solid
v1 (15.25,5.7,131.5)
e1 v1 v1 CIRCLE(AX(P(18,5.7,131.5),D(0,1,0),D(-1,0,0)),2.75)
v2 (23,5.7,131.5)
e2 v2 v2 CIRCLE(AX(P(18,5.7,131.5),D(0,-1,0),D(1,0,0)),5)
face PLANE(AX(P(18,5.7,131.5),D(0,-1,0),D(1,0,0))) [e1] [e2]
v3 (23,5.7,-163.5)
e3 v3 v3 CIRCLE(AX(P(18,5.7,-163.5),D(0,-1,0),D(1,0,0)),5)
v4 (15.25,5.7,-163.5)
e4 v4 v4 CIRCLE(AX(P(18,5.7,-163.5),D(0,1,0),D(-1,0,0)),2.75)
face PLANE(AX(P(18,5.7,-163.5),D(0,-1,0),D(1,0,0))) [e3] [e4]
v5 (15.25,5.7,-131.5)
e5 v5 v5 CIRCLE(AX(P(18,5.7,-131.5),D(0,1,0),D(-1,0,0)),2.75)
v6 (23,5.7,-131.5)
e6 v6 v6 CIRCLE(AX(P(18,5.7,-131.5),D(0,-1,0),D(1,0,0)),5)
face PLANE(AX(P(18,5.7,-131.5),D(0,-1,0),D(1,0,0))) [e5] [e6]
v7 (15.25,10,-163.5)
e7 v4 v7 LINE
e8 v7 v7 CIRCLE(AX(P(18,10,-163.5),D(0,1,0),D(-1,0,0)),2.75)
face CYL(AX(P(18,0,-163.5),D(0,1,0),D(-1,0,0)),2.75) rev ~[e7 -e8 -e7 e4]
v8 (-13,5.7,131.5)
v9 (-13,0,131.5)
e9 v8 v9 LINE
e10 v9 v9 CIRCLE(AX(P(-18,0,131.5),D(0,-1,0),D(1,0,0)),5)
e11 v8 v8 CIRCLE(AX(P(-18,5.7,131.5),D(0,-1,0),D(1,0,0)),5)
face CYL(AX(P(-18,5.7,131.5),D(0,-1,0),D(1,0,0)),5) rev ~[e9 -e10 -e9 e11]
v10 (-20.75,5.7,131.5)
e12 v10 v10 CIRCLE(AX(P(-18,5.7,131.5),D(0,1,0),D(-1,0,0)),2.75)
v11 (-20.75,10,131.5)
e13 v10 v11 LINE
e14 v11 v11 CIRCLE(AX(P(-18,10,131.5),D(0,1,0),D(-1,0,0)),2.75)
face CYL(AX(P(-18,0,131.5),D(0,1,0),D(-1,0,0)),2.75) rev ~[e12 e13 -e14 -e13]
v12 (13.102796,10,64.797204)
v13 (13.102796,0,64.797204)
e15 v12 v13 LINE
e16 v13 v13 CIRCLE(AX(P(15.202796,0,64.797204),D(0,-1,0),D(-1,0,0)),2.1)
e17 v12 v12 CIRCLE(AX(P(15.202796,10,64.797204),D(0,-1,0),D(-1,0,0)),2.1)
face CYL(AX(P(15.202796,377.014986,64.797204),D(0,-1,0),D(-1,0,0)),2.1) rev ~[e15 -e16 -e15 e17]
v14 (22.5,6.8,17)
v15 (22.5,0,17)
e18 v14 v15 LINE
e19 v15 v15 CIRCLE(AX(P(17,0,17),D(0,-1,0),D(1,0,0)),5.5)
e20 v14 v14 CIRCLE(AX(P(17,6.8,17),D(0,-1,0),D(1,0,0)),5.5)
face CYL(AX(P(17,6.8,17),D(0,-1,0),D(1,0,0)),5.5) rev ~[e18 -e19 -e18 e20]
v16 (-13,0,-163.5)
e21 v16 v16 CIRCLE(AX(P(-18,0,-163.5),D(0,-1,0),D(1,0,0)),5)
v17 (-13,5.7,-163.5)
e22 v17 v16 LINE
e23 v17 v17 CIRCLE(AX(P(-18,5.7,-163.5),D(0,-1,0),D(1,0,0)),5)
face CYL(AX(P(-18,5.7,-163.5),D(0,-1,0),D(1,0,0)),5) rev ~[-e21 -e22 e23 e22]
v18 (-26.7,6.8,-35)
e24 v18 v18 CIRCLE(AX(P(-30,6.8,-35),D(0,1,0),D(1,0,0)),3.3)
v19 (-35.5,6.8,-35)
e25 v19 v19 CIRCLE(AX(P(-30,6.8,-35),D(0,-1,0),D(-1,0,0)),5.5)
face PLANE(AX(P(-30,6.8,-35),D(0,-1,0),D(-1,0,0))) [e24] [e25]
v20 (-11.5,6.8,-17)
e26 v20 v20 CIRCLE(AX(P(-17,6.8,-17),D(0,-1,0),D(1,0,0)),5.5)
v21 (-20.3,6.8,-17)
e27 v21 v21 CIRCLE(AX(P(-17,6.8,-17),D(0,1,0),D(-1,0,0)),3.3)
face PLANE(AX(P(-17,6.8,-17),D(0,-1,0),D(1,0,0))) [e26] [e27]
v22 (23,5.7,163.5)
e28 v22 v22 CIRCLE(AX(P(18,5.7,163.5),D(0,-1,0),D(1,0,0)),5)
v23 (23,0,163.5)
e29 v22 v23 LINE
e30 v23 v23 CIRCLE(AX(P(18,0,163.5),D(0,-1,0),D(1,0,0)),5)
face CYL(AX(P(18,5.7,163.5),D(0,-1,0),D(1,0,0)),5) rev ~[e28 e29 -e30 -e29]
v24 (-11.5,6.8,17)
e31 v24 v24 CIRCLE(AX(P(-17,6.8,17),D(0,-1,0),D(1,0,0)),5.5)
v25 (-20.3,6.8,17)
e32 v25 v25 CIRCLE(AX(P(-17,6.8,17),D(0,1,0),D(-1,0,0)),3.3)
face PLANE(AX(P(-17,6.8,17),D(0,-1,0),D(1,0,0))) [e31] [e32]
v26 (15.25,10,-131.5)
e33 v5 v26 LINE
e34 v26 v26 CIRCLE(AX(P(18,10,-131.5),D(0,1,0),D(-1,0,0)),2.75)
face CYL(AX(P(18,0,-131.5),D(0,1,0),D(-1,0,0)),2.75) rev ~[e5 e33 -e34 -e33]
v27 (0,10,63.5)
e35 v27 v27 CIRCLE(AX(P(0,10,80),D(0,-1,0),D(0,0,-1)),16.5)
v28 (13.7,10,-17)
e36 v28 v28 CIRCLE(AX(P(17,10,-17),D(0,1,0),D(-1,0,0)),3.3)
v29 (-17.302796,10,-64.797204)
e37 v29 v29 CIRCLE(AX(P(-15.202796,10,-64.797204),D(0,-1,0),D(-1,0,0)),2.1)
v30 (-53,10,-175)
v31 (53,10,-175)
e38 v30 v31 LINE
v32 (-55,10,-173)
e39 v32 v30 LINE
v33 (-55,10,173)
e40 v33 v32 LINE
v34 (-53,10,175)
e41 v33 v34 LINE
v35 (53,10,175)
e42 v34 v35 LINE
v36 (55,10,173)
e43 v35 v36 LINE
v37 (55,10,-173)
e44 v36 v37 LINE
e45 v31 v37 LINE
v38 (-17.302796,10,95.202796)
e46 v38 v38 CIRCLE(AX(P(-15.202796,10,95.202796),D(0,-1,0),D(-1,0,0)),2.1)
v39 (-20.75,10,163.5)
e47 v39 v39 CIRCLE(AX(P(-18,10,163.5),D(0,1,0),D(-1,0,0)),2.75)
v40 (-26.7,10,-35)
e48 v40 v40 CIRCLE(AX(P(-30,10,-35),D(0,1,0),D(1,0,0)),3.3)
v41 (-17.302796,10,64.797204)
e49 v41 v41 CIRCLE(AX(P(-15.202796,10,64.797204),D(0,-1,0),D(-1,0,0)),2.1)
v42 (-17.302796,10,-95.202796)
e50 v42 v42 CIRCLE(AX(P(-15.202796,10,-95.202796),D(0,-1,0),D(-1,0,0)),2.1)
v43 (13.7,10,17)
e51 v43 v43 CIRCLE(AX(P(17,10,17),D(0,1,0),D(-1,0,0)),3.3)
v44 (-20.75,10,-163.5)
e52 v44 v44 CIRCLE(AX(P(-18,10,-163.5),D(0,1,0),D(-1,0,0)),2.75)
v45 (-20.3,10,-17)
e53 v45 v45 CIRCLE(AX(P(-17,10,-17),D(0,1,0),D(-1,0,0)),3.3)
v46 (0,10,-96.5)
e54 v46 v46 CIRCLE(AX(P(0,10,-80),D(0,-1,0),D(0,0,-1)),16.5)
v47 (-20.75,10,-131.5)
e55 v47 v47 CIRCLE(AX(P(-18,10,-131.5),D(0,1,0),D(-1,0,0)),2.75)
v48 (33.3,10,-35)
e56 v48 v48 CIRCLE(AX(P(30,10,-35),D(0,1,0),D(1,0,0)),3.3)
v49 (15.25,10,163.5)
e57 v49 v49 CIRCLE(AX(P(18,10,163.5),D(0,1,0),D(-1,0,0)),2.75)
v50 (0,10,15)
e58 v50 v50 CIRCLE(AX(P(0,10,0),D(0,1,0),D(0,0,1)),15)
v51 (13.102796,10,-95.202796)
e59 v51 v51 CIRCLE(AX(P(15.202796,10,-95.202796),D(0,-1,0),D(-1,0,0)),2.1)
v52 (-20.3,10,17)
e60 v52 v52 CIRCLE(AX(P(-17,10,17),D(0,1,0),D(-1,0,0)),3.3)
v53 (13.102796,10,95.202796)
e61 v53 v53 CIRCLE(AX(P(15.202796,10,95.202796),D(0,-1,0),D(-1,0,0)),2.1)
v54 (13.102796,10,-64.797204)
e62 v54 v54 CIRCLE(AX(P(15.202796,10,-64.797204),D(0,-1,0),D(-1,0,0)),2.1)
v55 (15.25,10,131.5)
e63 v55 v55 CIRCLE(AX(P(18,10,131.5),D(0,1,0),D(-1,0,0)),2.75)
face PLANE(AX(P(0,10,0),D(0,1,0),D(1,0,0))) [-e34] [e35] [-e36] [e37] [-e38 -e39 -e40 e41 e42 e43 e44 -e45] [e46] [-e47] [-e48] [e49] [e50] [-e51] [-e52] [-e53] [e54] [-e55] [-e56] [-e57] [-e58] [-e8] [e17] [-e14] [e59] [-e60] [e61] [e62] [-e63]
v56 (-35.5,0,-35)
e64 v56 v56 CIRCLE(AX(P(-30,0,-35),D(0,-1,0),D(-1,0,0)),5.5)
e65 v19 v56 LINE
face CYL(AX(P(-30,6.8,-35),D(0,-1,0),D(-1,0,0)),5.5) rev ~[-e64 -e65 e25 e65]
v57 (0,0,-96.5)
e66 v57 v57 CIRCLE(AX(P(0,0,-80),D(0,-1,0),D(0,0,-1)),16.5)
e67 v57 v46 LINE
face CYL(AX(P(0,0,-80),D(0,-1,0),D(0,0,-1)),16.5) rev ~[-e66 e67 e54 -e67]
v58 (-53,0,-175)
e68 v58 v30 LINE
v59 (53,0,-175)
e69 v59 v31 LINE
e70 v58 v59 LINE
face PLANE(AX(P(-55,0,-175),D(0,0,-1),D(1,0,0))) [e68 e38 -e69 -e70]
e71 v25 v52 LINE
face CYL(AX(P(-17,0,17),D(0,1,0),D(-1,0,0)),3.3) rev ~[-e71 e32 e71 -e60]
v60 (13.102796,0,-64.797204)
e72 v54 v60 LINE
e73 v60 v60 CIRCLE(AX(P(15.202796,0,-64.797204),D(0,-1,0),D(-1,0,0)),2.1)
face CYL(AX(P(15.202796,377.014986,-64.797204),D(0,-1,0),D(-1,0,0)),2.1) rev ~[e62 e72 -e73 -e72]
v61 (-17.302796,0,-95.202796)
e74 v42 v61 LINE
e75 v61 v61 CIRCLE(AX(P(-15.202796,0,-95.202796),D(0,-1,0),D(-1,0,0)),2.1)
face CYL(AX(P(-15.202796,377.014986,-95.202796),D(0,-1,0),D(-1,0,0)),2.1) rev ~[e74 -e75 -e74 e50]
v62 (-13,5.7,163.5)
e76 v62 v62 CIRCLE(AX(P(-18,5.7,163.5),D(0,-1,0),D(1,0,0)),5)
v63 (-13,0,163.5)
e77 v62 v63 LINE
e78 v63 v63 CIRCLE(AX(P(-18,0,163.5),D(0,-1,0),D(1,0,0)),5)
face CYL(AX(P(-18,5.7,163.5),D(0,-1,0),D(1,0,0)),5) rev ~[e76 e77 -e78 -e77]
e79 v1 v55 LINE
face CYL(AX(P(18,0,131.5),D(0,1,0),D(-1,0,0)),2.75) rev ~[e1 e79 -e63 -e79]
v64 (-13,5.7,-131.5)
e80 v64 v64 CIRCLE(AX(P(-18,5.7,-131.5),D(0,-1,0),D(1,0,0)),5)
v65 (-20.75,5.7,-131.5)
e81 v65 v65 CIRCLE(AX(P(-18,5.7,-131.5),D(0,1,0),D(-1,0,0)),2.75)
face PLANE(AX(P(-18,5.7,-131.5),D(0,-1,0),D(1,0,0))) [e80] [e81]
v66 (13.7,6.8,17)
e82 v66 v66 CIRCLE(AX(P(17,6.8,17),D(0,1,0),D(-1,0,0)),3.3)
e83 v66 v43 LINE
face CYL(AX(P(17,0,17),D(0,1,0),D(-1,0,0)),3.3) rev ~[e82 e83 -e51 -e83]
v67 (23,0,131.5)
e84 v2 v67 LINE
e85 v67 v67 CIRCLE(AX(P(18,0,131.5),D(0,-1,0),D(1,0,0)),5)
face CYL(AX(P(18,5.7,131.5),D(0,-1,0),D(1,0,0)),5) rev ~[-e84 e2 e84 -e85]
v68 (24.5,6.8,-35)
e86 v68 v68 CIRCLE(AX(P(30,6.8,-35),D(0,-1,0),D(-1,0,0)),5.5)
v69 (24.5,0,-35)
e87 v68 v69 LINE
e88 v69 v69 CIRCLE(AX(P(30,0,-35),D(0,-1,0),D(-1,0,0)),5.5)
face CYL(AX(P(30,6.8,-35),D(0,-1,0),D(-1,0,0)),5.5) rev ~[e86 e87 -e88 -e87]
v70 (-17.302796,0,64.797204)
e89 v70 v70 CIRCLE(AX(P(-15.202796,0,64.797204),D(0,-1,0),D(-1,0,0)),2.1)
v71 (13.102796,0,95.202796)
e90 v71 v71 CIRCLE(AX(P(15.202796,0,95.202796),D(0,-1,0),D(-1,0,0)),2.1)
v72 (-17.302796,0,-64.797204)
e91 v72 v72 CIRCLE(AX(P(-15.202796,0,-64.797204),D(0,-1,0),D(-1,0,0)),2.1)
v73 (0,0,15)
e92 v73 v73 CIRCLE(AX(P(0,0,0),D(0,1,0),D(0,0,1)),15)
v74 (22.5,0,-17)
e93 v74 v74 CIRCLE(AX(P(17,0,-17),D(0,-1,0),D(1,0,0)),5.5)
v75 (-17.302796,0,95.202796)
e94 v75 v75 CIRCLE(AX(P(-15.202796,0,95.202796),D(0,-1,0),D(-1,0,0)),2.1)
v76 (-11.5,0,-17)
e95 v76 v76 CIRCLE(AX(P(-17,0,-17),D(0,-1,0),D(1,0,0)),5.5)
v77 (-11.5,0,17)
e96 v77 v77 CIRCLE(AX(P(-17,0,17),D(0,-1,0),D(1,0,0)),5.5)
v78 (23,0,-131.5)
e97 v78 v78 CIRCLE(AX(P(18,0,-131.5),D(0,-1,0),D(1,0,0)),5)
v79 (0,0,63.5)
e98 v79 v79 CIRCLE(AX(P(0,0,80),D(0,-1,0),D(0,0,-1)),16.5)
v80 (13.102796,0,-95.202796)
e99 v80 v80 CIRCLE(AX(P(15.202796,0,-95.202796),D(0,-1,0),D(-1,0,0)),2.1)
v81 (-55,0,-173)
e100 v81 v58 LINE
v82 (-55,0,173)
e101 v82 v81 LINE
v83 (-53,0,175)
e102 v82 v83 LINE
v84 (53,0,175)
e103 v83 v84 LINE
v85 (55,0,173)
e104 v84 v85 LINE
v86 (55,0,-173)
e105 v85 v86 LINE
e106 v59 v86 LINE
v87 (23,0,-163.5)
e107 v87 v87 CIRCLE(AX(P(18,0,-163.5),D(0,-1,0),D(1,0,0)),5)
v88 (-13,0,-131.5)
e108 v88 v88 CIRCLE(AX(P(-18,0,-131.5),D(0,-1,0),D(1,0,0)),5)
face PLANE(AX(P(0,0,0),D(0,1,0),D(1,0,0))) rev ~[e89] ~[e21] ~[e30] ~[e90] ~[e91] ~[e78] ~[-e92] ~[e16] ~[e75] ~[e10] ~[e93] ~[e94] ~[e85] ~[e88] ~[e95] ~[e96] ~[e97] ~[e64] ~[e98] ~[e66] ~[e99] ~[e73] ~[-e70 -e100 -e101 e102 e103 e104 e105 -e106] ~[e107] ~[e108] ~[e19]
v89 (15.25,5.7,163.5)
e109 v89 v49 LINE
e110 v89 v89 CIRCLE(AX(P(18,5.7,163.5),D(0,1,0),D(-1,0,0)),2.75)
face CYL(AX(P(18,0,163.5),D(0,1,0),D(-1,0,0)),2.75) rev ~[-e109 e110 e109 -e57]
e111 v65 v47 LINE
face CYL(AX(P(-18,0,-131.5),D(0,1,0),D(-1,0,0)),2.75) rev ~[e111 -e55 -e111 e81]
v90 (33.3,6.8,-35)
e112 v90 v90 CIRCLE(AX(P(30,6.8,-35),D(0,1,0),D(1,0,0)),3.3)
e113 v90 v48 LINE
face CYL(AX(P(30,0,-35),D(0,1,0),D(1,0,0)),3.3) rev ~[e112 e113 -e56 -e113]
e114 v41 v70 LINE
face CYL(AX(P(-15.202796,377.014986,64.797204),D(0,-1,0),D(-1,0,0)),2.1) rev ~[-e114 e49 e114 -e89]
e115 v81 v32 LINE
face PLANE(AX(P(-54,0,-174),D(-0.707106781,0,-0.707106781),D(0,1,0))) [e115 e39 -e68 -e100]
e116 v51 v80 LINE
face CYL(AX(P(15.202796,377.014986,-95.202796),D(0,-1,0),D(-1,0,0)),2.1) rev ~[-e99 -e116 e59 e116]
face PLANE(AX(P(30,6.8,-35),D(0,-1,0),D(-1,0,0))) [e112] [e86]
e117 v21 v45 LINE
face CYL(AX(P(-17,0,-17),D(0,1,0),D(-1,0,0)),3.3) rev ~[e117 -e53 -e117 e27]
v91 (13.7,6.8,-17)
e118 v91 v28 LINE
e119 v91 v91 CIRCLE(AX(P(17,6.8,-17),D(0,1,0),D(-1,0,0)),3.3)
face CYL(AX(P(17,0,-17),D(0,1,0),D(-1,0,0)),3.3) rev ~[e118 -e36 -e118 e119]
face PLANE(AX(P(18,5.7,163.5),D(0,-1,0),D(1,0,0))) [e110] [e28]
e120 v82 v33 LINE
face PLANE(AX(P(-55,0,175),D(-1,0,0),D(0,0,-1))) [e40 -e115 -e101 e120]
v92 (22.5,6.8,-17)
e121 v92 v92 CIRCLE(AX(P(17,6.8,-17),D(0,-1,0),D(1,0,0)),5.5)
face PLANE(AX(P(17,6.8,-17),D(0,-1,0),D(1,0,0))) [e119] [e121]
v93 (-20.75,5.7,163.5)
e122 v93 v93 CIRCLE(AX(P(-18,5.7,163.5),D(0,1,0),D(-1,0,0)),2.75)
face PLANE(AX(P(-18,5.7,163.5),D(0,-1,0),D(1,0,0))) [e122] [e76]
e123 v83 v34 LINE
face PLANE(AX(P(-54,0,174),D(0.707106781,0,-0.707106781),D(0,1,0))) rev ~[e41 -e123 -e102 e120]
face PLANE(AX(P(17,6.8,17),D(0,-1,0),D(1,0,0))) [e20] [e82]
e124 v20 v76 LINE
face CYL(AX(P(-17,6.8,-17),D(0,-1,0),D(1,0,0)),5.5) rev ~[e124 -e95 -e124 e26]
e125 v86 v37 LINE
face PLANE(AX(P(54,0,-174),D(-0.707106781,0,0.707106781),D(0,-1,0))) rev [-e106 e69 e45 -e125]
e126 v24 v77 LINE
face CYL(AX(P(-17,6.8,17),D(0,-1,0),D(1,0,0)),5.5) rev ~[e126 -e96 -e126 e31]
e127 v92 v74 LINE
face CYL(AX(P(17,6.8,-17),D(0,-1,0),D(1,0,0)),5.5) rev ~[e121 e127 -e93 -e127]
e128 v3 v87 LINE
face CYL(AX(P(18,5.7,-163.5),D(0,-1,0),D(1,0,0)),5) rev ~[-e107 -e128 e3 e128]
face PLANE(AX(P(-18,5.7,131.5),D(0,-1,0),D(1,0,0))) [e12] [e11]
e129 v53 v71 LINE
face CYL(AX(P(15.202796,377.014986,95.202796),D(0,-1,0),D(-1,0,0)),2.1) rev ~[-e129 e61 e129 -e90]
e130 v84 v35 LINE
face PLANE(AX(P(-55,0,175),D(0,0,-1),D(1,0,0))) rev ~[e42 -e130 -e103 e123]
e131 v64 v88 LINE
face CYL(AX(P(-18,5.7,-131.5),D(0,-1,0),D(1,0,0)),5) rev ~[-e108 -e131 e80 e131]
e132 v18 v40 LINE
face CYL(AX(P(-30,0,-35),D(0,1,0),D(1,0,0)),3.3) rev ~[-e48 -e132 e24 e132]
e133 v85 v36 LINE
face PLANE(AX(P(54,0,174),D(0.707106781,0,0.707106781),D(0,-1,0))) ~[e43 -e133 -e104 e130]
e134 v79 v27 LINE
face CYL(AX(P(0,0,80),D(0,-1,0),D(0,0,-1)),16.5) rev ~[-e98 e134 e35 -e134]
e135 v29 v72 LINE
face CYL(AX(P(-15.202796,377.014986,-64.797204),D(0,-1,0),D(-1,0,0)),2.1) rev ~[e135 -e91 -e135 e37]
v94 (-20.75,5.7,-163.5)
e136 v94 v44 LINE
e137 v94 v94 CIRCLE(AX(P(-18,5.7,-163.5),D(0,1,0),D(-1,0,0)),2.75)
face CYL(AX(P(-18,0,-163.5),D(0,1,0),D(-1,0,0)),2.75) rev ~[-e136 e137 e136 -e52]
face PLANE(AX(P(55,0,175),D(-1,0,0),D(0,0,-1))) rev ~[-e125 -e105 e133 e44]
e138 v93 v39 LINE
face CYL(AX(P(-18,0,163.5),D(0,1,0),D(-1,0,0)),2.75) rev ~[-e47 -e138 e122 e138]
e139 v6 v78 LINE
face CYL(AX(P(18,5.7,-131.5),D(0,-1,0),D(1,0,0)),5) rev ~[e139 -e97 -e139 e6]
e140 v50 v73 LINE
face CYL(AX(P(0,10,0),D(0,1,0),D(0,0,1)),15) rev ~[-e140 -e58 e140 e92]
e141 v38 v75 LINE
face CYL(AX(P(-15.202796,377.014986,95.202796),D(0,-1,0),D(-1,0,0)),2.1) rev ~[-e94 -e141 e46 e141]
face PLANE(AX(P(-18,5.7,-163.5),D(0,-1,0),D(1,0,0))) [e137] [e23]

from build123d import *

# Parameters (mm, degrees)
SKETCH1_W                                         = 110
SKETCH1_H                                         = 350
BOSS_EXTRUDE1_DEPTH                               = 10
HOLE_SIZE_BY_SOCKET_HEAD_CAP_SCREW_TY_D           = 5.5
HOLE_SIZE_BY_SOCKET_HEAD_CAP_SCREW_TY_CBORE_D     = 10
HOLE_SIZE_BY_SOCKET_HEAD_CAP_SCREW_TY_CBORE_DEPTH = 5.7
HOLE_SIZE_BY_SOCKET_HEAD_CAP_SCRE_2_D             = 6.6
HOLE_SIZE_BY_SOCKET_HEAD_CAP_SCRE_2_CBORE_D       = 11
HOLE_SIZE_BY_SOCKET_HEAD_CAP_SCRE_2_CBORE_DEPTH   = 6.8
CHAMFER1_SIZE                                     = 2
HOLE_SIZE_BY_SOCKET_HEAD_CAP_SCRE_3_D             = 6.6
HOLE_SIZE_BY_SOCKET_HEAD_CAP_SCRE_3_CBORE_D       = 11
HOLE_SIZE_BY_SOCKET_HEAD_CAP_SCRE_3_CBORE_DEPTH   = 6.8
SKETCH8_R                                         = 16.5
CUT_EXTRUDE1_DEPTH                                = 184.711730709
M5_TAPPED_HOLE1_D                                 = 4.2
SKETCH11_R                                        = 15
CUT_EXTRUDE2_DEPTH                                = 184.711730709


with BuildPart() as part:
    # Sketch1 → Boss-Extrude1 (new body)
    with BuildSketch(Plane(origin=(0, 0, 0), x_dir=(1, 0, 0), z_dir=(0, 1, 0))):
        Rectangle(SKETCH1_W, SKETCH1_H)
    extrude(amount=BOSS_EXTRUDE1_DEPTH)

    # Hole Size _ by_ Socket Head Cap Screw Ty (through all)
    with Locations(Plane.XZ):
        with Locations((-18, 131.5), (18, 131.5), (18, 163.5), (-18, 163.5), (-18, -163.5), (-18, -131.5), (18, -163.5), (18, -131.5)):
            CounterBoreHole(HOLE_SIZE_BY_SOCKET_HEAD_CAP_SCREW_TY_D / 2, HOLE_SIZE_BY_SOCKET_HEAD_CAP_SCREW_TY_CBORE_D / 2, HOLE_SIZE_BY_SOCKET_HEAD_CAP_SCREW_TY_CBORE_DEPTH)

    # Hole Size _ by_ Socket Head Cap Scre 2 (through all)
    with Locations(Plane.XZ):
        with Locations((-17, -17), (17, -17), (17, 17), (-17, 17)):
            CounterBoreHole(HOLE_SIZE_BY_SOCKET_HEAD_CAP_SCRE_2_D / 2, HOLE_SIZE_BY_SOCKET_HEAD_CAP_SCRE_2_CBORE_D / 2, HOLE_SIZE_BY_SOCKET_HEAD_CAP_SCRE_2_CBORE_DEPTH)

    # Chamfer1
    chamfer1_edges = [part.edges().sort_by_distance(p)[0] for p in [
        (55, 5, 175),
        (-55, 5, 175),
        (-55, 5, -175),
        (55, 5, -175),
    ]]
    chamfer(chamfer1_edges, length=CHAMFER1_SIZE)

    # Hole Size _ by_ Socket Head Cap Scre 3 (through all)
    with Locations(Plane(origin=(0, 0, 0), x_dir=(-1, 0, 0), z_dir=(0, -1, 0))):
        with Locations((30, 35), (-30, 35)):
            CounterBoreHole(HOLE_SIZE_BY_SOCKET_HEAD_CAP_SCRE_3_D / 2, HOLE_SIZE_BY_SOCKET_HEAD_CAP_SCRE_3_CBORE_D / 2, HOLE_SIZE_BY_SOCKET_HEAD_CAP_SCRE_3_CBORE_DEPTH)

    # Sketch8 → Cut-Extrude1 (cut, through all)
    with BuildSketch(Plane.XZ):
        with Locations(Location((0, -80, 0), (0, 0, 270))):
            Circle(SKETCH8_R)
        with Locations(Location((0, 80, 0), (0, 0, 270))):
            Circle(SKETCH8_R)
    extrude(amount=-CUT_EXTRUDE1_DEPTH, mode=Mode.SUBTRACT)

    # M5 Tapped Hole1 (through all)
    with Locations(Plane(origin=(0, 10, 0), x_dir=(1, 0, 0), z_dir=(0, 1, 0))):
        with Locations((-15.202795796, 95.202795796), (15.202795796, 64.797204204), (-15.202795796, 64.797204204), (15.202795796, 95.202795796), (-15.202795796, -64.797204204), (15.202795796, -95.202795796), (15.202795796, -64.797204204), (-15.202795796, -95.202795796)):
            Hole(M5_TAPPED_HOLE1_D / 2)

    # Sketch11 → Cut-Extrude2 (cut, through all)
    with BuildSketch(Plane(origin=(0, 10, 0), x_dir=(1, 0, 0), z_dir=(0, 1, 0))):
        with Locations(Location((0, 0, 0), (0, 0, 270))):
            Circle(SKETCH11_R)
    extrude(amount=-CUT_EXTRUDE2_DEPTH, mode=Mode.SUBTRACT)


solid = part.part
